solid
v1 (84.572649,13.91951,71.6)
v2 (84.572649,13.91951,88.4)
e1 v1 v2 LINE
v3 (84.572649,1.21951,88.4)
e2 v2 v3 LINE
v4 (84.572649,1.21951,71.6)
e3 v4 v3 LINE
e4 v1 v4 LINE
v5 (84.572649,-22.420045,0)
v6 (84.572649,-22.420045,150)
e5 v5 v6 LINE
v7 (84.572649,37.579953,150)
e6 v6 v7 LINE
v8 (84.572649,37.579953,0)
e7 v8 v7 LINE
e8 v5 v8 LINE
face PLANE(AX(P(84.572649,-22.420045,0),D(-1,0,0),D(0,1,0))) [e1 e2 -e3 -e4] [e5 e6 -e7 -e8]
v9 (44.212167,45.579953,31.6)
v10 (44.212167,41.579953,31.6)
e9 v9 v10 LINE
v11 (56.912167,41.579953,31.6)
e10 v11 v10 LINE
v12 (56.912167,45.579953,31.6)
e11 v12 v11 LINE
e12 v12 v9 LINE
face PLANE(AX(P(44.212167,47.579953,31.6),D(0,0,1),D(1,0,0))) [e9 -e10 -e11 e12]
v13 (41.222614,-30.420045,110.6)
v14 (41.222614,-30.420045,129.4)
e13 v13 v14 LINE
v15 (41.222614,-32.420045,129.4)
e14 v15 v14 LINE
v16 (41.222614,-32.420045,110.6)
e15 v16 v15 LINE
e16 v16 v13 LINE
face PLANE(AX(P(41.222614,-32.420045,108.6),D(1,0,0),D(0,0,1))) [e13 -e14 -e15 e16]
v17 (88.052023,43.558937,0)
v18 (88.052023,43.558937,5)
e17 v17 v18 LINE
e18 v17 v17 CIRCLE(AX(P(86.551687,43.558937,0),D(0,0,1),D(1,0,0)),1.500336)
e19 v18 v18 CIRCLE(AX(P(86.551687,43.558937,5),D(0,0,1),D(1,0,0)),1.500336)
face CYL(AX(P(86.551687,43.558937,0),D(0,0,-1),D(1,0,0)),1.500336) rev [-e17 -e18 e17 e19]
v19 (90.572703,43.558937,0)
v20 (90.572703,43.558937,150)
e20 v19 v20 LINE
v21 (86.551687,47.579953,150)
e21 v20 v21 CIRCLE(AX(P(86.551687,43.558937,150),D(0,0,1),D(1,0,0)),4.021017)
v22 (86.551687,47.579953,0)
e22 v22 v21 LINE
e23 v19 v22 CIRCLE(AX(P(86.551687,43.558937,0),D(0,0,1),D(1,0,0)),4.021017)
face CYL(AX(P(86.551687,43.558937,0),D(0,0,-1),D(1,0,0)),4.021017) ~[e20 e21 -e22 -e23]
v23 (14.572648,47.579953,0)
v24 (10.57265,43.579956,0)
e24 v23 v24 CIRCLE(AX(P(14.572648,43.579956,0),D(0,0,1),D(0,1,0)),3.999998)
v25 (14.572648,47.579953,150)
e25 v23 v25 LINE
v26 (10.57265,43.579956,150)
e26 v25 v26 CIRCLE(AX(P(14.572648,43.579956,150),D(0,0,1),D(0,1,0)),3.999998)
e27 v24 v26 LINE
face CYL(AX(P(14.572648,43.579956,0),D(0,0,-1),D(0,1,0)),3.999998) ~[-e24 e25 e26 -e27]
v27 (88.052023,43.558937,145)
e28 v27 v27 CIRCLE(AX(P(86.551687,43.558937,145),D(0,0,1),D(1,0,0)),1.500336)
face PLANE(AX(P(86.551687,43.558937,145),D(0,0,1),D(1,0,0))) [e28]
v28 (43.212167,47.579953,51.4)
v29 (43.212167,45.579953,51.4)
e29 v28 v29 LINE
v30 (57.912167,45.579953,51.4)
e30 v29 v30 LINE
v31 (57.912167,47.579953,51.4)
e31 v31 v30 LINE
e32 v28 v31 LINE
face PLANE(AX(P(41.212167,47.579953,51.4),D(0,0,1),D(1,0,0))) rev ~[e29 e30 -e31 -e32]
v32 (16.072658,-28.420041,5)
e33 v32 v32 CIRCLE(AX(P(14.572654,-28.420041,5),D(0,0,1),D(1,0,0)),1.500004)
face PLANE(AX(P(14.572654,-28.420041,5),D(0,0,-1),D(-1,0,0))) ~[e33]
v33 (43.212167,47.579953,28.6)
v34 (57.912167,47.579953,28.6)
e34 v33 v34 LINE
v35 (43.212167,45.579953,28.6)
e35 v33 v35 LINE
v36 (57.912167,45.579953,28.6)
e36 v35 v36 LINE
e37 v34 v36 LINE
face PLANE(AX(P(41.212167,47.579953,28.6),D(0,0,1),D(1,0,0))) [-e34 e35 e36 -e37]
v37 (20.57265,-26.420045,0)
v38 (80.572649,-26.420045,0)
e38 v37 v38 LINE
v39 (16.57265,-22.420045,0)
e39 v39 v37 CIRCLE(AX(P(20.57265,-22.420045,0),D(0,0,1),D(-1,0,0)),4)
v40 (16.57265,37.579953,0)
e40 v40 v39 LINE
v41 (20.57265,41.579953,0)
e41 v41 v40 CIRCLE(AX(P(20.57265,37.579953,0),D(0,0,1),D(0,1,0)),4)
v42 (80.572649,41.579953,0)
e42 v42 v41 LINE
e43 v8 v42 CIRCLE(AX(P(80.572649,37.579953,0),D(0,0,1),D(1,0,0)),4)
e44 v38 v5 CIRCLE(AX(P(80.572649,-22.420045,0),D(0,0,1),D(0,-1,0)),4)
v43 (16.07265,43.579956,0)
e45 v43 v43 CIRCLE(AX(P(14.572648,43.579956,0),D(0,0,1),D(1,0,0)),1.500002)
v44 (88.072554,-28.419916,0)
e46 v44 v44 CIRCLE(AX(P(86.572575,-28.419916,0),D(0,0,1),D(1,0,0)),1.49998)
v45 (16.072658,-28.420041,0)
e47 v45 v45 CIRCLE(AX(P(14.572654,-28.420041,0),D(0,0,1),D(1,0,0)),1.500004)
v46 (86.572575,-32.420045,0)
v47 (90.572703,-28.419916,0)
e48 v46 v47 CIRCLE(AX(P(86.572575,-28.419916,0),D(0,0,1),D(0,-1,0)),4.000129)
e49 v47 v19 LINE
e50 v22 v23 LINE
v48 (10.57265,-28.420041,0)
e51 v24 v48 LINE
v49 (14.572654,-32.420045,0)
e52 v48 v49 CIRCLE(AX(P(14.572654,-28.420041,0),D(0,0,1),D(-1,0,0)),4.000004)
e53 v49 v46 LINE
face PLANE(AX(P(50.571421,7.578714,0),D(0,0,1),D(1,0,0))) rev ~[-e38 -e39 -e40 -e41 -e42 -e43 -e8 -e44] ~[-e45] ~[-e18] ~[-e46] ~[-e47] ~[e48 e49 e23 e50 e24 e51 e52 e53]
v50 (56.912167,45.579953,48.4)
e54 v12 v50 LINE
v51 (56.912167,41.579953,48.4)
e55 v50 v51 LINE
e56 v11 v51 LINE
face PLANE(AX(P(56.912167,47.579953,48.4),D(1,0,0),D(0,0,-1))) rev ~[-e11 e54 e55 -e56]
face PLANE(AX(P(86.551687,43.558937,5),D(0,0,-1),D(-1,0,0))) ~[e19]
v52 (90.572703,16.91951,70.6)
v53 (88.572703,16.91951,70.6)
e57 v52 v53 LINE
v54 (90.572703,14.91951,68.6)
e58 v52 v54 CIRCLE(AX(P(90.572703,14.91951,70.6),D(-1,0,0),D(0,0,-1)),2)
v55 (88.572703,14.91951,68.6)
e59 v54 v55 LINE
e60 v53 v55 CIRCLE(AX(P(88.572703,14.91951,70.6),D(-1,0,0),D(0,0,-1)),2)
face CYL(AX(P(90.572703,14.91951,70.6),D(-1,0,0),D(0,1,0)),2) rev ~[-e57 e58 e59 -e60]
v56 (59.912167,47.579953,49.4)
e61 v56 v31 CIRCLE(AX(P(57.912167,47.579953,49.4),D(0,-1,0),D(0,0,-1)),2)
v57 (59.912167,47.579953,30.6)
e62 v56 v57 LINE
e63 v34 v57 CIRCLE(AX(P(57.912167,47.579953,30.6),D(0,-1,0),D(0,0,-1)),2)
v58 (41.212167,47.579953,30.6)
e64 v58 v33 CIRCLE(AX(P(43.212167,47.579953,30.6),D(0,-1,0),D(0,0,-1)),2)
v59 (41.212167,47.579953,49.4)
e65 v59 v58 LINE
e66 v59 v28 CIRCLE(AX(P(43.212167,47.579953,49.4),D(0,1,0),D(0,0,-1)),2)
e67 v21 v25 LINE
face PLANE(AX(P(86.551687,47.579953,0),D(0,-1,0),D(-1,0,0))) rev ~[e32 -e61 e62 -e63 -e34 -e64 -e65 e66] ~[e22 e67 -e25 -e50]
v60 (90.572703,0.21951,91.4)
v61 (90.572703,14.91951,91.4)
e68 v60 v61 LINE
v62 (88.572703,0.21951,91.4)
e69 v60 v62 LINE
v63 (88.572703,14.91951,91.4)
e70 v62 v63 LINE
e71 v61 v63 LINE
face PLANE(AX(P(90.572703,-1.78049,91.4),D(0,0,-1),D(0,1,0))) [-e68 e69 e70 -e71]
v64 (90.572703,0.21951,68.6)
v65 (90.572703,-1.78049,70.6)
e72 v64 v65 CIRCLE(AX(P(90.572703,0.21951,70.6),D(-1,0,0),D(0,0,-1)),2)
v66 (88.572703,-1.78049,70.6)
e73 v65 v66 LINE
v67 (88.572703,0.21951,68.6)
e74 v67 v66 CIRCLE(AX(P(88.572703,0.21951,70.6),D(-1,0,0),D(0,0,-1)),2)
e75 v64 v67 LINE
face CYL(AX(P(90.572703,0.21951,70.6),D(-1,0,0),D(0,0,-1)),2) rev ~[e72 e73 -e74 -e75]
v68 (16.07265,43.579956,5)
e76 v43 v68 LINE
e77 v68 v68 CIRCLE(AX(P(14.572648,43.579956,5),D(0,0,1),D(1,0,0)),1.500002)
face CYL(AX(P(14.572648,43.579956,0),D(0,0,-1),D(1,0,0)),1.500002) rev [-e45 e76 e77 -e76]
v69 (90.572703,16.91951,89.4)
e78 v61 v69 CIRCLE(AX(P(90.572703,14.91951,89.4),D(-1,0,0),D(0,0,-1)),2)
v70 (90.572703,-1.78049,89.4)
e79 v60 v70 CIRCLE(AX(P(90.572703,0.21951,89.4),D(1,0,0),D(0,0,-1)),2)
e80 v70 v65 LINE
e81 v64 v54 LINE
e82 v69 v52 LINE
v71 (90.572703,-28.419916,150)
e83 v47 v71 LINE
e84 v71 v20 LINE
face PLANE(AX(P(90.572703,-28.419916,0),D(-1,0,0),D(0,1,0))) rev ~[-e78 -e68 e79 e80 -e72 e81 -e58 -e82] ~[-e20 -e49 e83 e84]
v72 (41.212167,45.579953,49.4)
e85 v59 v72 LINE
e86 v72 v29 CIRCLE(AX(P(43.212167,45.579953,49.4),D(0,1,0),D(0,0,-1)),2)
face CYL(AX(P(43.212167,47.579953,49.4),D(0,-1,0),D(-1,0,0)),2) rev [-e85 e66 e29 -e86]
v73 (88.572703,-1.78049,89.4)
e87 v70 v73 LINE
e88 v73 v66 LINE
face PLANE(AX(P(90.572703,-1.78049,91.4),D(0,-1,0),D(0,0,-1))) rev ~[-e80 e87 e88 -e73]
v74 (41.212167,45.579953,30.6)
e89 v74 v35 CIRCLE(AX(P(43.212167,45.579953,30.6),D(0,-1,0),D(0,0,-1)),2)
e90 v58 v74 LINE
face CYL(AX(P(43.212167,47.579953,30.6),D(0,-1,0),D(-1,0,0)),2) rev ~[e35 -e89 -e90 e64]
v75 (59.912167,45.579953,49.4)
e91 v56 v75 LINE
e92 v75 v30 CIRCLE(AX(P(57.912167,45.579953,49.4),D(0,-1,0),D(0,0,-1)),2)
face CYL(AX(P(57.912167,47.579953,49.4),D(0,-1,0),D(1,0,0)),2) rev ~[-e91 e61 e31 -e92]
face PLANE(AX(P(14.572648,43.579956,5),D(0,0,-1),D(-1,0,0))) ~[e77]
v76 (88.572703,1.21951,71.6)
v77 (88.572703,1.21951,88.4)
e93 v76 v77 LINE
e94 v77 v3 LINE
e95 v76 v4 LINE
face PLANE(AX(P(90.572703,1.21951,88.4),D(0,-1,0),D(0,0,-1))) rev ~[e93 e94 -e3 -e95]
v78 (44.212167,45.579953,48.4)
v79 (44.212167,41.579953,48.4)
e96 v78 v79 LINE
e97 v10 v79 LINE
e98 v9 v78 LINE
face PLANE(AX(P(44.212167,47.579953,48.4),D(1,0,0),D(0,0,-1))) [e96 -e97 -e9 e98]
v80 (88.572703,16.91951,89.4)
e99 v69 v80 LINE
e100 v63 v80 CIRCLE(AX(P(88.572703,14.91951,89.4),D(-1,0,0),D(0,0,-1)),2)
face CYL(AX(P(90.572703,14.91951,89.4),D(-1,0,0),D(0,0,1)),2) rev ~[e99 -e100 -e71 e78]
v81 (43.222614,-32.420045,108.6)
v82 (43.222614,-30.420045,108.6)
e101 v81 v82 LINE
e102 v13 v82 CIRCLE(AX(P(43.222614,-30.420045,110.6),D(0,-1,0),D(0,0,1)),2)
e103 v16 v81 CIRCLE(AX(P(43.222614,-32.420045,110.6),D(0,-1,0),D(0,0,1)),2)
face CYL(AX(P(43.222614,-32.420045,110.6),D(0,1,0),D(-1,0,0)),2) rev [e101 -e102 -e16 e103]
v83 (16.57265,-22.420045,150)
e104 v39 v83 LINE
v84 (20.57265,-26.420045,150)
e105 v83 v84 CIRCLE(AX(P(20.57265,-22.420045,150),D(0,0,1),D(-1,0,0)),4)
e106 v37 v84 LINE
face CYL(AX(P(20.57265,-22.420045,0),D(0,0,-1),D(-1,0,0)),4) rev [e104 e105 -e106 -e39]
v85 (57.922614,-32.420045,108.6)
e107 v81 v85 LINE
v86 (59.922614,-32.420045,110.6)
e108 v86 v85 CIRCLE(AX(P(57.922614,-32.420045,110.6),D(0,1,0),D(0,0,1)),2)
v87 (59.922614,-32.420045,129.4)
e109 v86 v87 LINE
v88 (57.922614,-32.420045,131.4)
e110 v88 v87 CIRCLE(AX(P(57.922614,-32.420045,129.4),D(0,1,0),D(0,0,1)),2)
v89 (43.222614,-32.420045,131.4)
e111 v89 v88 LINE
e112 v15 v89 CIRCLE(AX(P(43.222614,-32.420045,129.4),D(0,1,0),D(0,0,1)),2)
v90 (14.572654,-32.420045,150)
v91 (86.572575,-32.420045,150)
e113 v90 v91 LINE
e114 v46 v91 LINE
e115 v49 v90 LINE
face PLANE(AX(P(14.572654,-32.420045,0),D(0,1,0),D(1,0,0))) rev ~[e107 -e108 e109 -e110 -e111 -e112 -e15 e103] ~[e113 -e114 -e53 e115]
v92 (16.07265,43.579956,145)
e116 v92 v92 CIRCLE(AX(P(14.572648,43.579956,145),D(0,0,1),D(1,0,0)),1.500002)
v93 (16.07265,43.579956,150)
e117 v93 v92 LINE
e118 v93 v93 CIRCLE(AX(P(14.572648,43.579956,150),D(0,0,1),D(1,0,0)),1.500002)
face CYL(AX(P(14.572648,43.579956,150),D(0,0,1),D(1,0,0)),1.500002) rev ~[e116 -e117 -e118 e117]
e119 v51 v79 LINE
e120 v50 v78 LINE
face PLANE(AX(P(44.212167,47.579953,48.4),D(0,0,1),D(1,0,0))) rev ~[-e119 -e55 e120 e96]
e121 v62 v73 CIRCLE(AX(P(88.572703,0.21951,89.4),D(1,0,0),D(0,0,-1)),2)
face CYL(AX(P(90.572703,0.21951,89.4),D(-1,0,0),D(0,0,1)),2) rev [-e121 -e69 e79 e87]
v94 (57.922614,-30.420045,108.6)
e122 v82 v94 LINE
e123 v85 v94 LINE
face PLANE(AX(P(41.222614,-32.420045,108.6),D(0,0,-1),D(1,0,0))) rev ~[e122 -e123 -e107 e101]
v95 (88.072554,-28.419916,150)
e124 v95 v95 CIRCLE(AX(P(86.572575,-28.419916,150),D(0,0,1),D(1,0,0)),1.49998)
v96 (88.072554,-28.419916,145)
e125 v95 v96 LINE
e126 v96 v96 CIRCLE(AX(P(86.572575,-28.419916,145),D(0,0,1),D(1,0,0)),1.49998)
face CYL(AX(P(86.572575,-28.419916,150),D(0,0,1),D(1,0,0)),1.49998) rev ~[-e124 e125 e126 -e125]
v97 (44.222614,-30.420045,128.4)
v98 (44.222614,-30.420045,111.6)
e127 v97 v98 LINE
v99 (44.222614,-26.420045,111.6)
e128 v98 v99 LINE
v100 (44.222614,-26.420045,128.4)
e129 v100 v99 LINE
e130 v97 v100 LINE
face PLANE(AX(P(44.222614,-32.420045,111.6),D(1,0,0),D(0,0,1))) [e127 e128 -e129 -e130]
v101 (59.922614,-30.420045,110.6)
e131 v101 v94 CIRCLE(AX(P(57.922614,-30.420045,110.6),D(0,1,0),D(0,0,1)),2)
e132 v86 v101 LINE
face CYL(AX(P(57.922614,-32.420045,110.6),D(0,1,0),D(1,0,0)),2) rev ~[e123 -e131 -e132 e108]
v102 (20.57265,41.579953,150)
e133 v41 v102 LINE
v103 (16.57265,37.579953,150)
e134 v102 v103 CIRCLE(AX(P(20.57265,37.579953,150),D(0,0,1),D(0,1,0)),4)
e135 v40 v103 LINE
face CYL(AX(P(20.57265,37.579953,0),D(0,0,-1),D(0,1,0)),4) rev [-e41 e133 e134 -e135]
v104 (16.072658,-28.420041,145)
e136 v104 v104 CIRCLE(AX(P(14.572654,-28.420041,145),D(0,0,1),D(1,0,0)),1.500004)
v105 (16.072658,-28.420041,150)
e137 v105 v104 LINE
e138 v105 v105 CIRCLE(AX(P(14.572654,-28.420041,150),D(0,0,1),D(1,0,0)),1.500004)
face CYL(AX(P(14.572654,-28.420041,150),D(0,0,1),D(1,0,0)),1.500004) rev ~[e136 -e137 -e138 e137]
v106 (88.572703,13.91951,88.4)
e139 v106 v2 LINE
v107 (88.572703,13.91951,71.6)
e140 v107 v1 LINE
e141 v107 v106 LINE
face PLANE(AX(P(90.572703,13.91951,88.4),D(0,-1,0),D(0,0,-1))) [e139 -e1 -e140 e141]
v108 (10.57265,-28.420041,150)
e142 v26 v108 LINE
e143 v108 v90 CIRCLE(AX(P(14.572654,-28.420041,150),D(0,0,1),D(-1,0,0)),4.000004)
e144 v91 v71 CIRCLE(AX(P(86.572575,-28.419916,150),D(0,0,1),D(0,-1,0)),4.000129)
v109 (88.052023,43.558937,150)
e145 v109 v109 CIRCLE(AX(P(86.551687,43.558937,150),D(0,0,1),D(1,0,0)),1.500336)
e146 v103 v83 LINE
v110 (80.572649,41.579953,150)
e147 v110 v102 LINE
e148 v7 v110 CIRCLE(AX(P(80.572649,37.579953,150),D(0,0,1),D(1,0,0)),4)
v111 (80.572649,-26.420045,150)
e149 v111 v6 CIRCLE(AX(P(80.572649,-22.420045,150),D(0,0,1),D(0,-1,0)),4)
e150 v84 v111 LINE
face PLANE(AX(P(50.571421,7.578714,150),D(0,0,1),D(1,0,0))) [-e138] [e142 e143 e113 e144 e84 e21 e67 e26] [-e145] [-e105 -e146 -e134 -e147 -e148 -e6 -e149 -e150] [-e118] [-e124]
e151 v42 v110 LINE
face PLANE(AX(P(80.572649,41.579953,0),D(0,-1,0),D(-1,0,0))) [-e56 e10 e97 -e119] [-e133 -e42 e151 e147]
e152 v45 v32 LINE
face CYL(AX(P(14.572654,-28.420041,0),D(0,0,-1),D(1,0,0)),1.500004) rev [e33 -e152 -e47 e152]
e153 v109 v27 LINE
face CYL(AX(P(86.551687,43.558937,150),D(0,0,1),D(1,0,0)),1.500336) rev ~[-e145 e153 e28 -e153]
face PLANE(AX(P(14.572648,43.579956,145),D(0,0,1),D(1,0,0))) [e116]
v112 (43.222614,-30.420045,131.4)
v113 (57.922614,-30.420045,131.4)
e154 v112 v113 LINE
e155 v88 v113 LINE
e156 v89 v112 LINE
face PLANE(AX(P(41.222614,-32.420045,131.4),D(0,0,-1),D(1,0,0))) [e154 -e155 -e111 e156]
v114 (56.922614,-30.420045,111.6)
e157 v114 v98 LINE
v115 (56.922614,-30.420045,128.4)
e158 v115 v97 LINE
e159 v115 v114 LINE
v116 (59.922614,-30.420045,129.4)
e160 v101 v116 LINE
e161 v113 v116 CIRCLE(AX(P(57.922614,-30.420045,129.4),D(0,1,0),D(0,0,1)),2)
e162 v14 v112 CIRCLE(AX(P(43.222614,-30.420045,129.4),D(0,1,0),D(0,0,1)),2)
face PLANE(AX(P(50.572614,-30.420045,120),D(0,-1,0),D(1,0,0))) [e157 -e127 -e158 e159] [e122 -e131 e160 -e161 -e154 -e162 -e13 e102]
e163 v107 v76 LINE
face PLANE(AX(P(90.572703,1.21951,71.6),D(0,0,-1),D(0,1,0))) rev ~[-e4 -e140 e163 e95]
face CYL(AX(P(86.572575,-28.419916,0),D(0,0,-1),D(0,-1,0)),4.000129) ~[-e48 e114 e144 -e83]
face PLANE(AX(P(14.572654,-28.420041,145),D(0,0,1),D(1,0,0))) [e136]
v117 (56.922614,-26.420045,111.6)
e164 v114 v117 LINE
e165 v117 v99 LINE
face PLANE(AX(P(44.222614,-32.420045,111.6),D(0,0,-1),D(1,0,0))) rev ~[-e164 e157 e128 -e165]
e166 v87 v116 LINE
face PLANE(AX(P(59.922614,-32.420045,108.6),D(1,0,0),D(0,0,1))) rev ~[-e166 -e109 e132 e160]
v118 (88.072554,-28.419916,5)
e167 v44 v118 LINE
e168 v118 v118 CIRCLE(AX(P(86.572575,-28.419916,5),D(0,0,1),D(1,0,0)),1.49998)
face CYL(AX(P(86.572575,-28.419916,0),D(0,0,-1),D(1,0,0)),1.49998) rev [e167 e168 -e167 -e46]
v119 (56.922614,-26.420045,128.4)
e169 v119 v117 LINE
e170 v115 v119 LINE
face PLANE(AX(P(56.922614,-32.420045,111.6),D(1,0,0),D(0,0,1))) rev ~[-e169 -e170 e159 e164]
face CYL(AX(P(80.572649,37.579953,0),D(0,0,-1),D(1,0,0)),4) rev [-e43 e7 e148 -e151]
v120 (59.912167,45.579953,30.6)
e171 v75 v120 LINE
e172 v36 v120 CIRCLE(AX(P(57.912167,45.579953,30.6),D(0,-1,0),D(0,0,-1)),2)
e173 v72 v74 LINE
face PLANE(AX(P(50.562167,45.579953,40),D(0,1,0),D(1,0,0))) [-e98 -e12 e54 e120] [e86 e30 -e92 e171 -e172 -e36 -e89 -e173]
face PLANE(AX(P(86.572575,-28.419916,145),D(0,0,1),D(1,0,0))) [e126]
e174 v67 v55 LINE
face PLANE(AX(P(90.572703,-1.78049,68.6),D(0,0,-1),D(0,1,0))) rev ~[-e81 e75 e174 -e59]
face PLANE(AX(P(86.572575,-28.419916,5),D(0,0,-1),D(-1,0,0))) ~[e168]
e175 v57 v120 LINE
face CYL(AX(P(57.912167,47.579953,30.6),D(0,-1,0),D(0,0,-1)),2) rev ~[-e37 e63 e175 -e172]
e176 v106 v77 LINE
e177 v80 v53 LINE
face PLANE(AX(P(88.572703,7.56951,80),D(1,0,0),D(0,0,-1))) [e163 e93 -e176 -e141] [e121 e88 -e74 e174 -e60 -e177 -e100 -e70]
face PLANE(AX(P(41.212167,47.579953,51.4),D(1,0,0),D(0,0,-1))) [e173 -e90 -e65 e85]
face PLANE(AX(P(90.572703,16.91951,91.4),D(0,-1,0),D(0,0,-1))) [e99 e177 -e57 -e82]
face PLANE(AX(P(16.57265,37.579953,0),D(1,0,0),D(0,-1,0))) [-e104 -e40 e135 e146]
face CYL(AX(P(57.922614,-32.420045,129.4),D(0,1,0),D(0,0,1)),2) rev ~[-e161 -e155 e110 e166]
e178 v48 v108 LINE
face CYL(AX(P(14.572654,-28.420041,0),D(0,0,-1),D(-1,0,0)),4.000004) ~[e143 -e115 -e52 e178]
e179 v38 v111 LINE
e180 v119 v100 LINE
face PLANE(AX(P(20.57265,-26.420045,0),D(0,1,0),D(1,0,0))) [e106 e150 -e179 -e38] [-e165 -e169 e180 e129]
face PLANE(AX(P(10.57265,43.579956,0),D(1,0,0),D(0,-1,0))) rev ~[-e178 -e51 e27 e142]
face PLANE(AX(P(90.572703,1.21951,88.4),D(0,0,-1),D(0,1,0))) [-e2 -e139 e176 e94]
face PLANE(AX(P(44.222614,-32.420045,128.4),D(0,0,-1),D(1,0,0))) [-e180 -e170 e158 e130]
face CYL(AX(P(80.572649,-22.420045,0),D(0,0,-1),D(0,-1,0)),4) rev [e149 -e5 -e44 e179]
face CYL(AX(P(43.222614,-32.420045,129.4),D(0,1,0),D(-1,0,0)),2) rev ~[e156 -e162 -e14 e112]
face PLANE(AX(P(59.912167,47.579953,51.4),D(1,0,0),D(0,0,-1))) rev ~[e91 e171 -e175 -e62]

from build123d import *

# Parameters (mm, degrees)
BOSS_EXTRUDE1_DEPTH = 150
SKETCH2_R           = 1.500003704
SKETCH2_R_2         = 1.500002005
SKETCH2_R_3         = 1.500336032
SKETCH2_R_4         = 1.499979566
CUT_EXTRUDE1_DEPTH  = 5
SKETCH7_W           = 12.7
SKETCH7_H           = 16.8
CUT_EXTRUDE2_DEPTH  = 13
SKETCH8_W           = 16.8
SKETCH8_H           = 12.7
CUT_EXTRUDE3_DEPTH  = 13
SKETCH9_W           = 12.7
SKETCH9_H           = 16.8
CUT_EXTRUDE4_DEPTH  = 13
SKETCH10_W          = 18.7
SKETCH10_H          = 22.8
CUT_EXTRUDE5_DEPTH  = 2
FILLET1_R           = 2
SKETCH12_W          = 22.8
SKETCH12_H          = 18.7
CUT_EXTRUDE6_DEPTH  = 2
FILLET2_R           = 2
SKETCH13_W          = 18.7
SKETCH13_H          = 22.8
CUT_EXTRUDE7_DEPTH  = 2
FILLET3_R           = 2


with BuildPart() as part:
    # Sketch1 → Boss-Extrude1 (new body)
    with BuildSketch(Plane.XY):
        with BuildLine():
            Line((10.572650429, 43.57995567), (10.572650429, -28.420041122))
            ThreePointArc((10.572650429, -28.420041122), (11.744224426, -31.248470954), (14.572654257, -32.420044951))
            Line((14.572654257, -32.420044951), (86.572574673, -32.420044951))
            ThreePointArc((86.572574673, -32.420044951), (89.401092734, -31.248434409), (90.572703276, -28.419916348))
            Line((90.572703276, -28.419916348), (90.572703276, 43.558936727))
            ThreePointArc((90.572703276, 43.558936727), (89.3949748, 46.402224786), (86.551686742, 47.579953261))
            Line((86.551686742, 47.579953261), (14.57264802, 47.579953261))
            ThreePointArc((14.57264802, 47.579953261), (11.744222599, 46.408381091), (10.572650429, 43.57995567))
        make_face()
        with BuildLine():
            Line((16.572650429, 37.579953261), (16.572650429, -22.420044951))
            ThreePointArc((16.572650429, -22.420044951), (17.744223304, -25.248472075), (20.572650429, -26.420044951))
            Line((20.572650429, -26.420044951), (80.572648641, -26.420044951))
            ThreePointArc((80.572648641, -26.420044951), (83.401075766, -25.248472075), (84.572648641, -22.420044951))
            Line((84.572648641, -22.420044951), (84.572648641, 37.579953261))
            ThreePointArc((84.572648641, 37.579953261), (83.401075766, 40.408380386), (80.572648641, 41.579953261))
            Line((80.572648641, 41.579953261), (20.572650429, 41.579953261))
            ThreePointArc((20.572650429, 41.579953261), (17.744223304, 40.408380386), (16.572650429, 37.579953261))
        make_face(mode=Mode.SUBTRACT)
    extrude(amount=BOSS_EXTRUDE1_DEPTH)

    # Sketch2 → Cut-Extrude1 (cut)
    with BuildSketch(Plane.XY.offset(150)):
        with Locations((14.572654257, -28.420041122)):
            Circle(SKETCH2_R)
        with Locations((14.57264802, 43.57995567)):
            Circle(SKETCH2_R_2)
        with Locations((86.551686742, 43.558936727)):
            Circle(SKETCH2_R_3)
        with Locations((86.572574673, -28.419916348)):
            Circle(SKETCH2_R_4)
    cut_extrude1 = extrude(amount=-CUT_EXTRUDE1_DEPTH, mode=Mode.SUBTRACT)

    # Mirror1: Cut-Extrude1 across plane
    add(cut_extrude1.mirror(Plane(origin=(0, 0, 75), x_dir=(1, 0, 0), z_dir=(0, 0, -1))), mode=Mode.SUBTRACT)

    # Sketch7 → Cut-Extrude2 (cut)
    with BuildSketch(Plane(origin=(0, 47.579953261, 0), x_dir=(1, 0, 0), z_dir=(0, 1, 0))):
        with Locations((50.562167381, -40)):
            Rectangle(SKETCH7_W, SKETCH7_H)
    extrude(amount=-CUT_EXTRUDE2_DEPTH, mode=Mode.SUBTRACT)

    # Sketch8 → Cut-Extrude3 (cut)
    with BuildSketch(Plane(origin=(90.572703276, 0, 0), x_dir=(0, 0, -1), z_dir=(1, 0, 0))):
        with Locations((-80, 7.569510189)):
            Rectangle(SKETCH8_W, SKETCH8_H)
    extrude(amount=-CUT_EXTRUDE3_DEPTH, mode=Mode.SUBTRACT)

    # Sketch9 → Cut-Extrude4 (cut)
    with BuildSketch(Plane.XZ.offset(32.420044951)):
        with Locations((50.572614465, 120)):
            Rectangle(SKETCH9_W, SKETCH9_H)
    extrude(amount=-CUT_EXTRUDE4_DEPTH, mode=Mode.SUBTRACT)

    # Sketch10 → Cut-Extrude5 (cut)
    with BuildSketch(Plane(origin=(0, 47.579953261, 0), x_dir=(1, 0, 0), z_dir=(0, 1, 0))):
        with Locations((50.562167381, -40)):
            Rectangle(SKETCH10_W, SKETCH10_H)
    extrude(amount=-CUT_EXTRUDE5_DEPTH, mode=Mode.SUBTRACT)

    # Fillet1
    fillet1_edges = [part.edges().sort_by_distance(p)[0] for p in [
        (59.912167381, 46.579953261, 28.6),
        (59.912167381, 46.579953261, 51.4),
        (41.212167381, 46.579953261, 51.4),
        (41.212167381, 46.579953261, 28.6),
    ]]
    fillet(fillet1_edges, radius=FILLET1_R)

    # Sketch12 → Cut-Extrude6 (cut)
    with BuildSketch(Plane(origin=(90.572703276, 0, 0), x_dir=(0, 0, -1), z_dir=(1, 0, 0))):
        with Locations((-80, 7.569510189)):
            Rectangle(SKETCH12_W, SKETCH12_H)
    extrude(amount=-CUT_EXTRUDE6_DEPTH, mode=Mode.SUBTRACT)

    # Fillet2
    fillet2_edges = [part.edges().sort_by_distance(p)[0] for p in [
        (89.572703276, 16.919510189, 91.4),
        (89.572703276, 16.919510189, 68.6),
        (89.572703276, -1.780489811, 68.6),
        (89.572703276, -1.780489811, 91.4),
    ]]
    fillet(fillet2_edges, radius=FILLET2_R)

    # Sketch13 → Cut-Extrude7 (cut)
    with BuildSketch(Plane.XZ.offset(32.420044951)):
        with Locations((50.572614465, 120)):
            Rectangle(SKETCH13_W, SKETCH13_H)
    extrude(amount=-CUT_EXTRUDE7_DEPTH, mode=Mode.SUBTRACT)

    # Fillet3
    fillet3_edges = [part.edges().sort_by_distance(p)[0] for p in [
        (41.222614465, -31.420044951, 108.6),
        (41.222614465, -31.420044951, 131.4),
        (59.922614465, -31.420044951, 131.4),
        (59.922614465, -31.420044951, 108.6),
    ]]
    fillet(fillet3_edges, radius=FILLET3_R)


solid = part.part
